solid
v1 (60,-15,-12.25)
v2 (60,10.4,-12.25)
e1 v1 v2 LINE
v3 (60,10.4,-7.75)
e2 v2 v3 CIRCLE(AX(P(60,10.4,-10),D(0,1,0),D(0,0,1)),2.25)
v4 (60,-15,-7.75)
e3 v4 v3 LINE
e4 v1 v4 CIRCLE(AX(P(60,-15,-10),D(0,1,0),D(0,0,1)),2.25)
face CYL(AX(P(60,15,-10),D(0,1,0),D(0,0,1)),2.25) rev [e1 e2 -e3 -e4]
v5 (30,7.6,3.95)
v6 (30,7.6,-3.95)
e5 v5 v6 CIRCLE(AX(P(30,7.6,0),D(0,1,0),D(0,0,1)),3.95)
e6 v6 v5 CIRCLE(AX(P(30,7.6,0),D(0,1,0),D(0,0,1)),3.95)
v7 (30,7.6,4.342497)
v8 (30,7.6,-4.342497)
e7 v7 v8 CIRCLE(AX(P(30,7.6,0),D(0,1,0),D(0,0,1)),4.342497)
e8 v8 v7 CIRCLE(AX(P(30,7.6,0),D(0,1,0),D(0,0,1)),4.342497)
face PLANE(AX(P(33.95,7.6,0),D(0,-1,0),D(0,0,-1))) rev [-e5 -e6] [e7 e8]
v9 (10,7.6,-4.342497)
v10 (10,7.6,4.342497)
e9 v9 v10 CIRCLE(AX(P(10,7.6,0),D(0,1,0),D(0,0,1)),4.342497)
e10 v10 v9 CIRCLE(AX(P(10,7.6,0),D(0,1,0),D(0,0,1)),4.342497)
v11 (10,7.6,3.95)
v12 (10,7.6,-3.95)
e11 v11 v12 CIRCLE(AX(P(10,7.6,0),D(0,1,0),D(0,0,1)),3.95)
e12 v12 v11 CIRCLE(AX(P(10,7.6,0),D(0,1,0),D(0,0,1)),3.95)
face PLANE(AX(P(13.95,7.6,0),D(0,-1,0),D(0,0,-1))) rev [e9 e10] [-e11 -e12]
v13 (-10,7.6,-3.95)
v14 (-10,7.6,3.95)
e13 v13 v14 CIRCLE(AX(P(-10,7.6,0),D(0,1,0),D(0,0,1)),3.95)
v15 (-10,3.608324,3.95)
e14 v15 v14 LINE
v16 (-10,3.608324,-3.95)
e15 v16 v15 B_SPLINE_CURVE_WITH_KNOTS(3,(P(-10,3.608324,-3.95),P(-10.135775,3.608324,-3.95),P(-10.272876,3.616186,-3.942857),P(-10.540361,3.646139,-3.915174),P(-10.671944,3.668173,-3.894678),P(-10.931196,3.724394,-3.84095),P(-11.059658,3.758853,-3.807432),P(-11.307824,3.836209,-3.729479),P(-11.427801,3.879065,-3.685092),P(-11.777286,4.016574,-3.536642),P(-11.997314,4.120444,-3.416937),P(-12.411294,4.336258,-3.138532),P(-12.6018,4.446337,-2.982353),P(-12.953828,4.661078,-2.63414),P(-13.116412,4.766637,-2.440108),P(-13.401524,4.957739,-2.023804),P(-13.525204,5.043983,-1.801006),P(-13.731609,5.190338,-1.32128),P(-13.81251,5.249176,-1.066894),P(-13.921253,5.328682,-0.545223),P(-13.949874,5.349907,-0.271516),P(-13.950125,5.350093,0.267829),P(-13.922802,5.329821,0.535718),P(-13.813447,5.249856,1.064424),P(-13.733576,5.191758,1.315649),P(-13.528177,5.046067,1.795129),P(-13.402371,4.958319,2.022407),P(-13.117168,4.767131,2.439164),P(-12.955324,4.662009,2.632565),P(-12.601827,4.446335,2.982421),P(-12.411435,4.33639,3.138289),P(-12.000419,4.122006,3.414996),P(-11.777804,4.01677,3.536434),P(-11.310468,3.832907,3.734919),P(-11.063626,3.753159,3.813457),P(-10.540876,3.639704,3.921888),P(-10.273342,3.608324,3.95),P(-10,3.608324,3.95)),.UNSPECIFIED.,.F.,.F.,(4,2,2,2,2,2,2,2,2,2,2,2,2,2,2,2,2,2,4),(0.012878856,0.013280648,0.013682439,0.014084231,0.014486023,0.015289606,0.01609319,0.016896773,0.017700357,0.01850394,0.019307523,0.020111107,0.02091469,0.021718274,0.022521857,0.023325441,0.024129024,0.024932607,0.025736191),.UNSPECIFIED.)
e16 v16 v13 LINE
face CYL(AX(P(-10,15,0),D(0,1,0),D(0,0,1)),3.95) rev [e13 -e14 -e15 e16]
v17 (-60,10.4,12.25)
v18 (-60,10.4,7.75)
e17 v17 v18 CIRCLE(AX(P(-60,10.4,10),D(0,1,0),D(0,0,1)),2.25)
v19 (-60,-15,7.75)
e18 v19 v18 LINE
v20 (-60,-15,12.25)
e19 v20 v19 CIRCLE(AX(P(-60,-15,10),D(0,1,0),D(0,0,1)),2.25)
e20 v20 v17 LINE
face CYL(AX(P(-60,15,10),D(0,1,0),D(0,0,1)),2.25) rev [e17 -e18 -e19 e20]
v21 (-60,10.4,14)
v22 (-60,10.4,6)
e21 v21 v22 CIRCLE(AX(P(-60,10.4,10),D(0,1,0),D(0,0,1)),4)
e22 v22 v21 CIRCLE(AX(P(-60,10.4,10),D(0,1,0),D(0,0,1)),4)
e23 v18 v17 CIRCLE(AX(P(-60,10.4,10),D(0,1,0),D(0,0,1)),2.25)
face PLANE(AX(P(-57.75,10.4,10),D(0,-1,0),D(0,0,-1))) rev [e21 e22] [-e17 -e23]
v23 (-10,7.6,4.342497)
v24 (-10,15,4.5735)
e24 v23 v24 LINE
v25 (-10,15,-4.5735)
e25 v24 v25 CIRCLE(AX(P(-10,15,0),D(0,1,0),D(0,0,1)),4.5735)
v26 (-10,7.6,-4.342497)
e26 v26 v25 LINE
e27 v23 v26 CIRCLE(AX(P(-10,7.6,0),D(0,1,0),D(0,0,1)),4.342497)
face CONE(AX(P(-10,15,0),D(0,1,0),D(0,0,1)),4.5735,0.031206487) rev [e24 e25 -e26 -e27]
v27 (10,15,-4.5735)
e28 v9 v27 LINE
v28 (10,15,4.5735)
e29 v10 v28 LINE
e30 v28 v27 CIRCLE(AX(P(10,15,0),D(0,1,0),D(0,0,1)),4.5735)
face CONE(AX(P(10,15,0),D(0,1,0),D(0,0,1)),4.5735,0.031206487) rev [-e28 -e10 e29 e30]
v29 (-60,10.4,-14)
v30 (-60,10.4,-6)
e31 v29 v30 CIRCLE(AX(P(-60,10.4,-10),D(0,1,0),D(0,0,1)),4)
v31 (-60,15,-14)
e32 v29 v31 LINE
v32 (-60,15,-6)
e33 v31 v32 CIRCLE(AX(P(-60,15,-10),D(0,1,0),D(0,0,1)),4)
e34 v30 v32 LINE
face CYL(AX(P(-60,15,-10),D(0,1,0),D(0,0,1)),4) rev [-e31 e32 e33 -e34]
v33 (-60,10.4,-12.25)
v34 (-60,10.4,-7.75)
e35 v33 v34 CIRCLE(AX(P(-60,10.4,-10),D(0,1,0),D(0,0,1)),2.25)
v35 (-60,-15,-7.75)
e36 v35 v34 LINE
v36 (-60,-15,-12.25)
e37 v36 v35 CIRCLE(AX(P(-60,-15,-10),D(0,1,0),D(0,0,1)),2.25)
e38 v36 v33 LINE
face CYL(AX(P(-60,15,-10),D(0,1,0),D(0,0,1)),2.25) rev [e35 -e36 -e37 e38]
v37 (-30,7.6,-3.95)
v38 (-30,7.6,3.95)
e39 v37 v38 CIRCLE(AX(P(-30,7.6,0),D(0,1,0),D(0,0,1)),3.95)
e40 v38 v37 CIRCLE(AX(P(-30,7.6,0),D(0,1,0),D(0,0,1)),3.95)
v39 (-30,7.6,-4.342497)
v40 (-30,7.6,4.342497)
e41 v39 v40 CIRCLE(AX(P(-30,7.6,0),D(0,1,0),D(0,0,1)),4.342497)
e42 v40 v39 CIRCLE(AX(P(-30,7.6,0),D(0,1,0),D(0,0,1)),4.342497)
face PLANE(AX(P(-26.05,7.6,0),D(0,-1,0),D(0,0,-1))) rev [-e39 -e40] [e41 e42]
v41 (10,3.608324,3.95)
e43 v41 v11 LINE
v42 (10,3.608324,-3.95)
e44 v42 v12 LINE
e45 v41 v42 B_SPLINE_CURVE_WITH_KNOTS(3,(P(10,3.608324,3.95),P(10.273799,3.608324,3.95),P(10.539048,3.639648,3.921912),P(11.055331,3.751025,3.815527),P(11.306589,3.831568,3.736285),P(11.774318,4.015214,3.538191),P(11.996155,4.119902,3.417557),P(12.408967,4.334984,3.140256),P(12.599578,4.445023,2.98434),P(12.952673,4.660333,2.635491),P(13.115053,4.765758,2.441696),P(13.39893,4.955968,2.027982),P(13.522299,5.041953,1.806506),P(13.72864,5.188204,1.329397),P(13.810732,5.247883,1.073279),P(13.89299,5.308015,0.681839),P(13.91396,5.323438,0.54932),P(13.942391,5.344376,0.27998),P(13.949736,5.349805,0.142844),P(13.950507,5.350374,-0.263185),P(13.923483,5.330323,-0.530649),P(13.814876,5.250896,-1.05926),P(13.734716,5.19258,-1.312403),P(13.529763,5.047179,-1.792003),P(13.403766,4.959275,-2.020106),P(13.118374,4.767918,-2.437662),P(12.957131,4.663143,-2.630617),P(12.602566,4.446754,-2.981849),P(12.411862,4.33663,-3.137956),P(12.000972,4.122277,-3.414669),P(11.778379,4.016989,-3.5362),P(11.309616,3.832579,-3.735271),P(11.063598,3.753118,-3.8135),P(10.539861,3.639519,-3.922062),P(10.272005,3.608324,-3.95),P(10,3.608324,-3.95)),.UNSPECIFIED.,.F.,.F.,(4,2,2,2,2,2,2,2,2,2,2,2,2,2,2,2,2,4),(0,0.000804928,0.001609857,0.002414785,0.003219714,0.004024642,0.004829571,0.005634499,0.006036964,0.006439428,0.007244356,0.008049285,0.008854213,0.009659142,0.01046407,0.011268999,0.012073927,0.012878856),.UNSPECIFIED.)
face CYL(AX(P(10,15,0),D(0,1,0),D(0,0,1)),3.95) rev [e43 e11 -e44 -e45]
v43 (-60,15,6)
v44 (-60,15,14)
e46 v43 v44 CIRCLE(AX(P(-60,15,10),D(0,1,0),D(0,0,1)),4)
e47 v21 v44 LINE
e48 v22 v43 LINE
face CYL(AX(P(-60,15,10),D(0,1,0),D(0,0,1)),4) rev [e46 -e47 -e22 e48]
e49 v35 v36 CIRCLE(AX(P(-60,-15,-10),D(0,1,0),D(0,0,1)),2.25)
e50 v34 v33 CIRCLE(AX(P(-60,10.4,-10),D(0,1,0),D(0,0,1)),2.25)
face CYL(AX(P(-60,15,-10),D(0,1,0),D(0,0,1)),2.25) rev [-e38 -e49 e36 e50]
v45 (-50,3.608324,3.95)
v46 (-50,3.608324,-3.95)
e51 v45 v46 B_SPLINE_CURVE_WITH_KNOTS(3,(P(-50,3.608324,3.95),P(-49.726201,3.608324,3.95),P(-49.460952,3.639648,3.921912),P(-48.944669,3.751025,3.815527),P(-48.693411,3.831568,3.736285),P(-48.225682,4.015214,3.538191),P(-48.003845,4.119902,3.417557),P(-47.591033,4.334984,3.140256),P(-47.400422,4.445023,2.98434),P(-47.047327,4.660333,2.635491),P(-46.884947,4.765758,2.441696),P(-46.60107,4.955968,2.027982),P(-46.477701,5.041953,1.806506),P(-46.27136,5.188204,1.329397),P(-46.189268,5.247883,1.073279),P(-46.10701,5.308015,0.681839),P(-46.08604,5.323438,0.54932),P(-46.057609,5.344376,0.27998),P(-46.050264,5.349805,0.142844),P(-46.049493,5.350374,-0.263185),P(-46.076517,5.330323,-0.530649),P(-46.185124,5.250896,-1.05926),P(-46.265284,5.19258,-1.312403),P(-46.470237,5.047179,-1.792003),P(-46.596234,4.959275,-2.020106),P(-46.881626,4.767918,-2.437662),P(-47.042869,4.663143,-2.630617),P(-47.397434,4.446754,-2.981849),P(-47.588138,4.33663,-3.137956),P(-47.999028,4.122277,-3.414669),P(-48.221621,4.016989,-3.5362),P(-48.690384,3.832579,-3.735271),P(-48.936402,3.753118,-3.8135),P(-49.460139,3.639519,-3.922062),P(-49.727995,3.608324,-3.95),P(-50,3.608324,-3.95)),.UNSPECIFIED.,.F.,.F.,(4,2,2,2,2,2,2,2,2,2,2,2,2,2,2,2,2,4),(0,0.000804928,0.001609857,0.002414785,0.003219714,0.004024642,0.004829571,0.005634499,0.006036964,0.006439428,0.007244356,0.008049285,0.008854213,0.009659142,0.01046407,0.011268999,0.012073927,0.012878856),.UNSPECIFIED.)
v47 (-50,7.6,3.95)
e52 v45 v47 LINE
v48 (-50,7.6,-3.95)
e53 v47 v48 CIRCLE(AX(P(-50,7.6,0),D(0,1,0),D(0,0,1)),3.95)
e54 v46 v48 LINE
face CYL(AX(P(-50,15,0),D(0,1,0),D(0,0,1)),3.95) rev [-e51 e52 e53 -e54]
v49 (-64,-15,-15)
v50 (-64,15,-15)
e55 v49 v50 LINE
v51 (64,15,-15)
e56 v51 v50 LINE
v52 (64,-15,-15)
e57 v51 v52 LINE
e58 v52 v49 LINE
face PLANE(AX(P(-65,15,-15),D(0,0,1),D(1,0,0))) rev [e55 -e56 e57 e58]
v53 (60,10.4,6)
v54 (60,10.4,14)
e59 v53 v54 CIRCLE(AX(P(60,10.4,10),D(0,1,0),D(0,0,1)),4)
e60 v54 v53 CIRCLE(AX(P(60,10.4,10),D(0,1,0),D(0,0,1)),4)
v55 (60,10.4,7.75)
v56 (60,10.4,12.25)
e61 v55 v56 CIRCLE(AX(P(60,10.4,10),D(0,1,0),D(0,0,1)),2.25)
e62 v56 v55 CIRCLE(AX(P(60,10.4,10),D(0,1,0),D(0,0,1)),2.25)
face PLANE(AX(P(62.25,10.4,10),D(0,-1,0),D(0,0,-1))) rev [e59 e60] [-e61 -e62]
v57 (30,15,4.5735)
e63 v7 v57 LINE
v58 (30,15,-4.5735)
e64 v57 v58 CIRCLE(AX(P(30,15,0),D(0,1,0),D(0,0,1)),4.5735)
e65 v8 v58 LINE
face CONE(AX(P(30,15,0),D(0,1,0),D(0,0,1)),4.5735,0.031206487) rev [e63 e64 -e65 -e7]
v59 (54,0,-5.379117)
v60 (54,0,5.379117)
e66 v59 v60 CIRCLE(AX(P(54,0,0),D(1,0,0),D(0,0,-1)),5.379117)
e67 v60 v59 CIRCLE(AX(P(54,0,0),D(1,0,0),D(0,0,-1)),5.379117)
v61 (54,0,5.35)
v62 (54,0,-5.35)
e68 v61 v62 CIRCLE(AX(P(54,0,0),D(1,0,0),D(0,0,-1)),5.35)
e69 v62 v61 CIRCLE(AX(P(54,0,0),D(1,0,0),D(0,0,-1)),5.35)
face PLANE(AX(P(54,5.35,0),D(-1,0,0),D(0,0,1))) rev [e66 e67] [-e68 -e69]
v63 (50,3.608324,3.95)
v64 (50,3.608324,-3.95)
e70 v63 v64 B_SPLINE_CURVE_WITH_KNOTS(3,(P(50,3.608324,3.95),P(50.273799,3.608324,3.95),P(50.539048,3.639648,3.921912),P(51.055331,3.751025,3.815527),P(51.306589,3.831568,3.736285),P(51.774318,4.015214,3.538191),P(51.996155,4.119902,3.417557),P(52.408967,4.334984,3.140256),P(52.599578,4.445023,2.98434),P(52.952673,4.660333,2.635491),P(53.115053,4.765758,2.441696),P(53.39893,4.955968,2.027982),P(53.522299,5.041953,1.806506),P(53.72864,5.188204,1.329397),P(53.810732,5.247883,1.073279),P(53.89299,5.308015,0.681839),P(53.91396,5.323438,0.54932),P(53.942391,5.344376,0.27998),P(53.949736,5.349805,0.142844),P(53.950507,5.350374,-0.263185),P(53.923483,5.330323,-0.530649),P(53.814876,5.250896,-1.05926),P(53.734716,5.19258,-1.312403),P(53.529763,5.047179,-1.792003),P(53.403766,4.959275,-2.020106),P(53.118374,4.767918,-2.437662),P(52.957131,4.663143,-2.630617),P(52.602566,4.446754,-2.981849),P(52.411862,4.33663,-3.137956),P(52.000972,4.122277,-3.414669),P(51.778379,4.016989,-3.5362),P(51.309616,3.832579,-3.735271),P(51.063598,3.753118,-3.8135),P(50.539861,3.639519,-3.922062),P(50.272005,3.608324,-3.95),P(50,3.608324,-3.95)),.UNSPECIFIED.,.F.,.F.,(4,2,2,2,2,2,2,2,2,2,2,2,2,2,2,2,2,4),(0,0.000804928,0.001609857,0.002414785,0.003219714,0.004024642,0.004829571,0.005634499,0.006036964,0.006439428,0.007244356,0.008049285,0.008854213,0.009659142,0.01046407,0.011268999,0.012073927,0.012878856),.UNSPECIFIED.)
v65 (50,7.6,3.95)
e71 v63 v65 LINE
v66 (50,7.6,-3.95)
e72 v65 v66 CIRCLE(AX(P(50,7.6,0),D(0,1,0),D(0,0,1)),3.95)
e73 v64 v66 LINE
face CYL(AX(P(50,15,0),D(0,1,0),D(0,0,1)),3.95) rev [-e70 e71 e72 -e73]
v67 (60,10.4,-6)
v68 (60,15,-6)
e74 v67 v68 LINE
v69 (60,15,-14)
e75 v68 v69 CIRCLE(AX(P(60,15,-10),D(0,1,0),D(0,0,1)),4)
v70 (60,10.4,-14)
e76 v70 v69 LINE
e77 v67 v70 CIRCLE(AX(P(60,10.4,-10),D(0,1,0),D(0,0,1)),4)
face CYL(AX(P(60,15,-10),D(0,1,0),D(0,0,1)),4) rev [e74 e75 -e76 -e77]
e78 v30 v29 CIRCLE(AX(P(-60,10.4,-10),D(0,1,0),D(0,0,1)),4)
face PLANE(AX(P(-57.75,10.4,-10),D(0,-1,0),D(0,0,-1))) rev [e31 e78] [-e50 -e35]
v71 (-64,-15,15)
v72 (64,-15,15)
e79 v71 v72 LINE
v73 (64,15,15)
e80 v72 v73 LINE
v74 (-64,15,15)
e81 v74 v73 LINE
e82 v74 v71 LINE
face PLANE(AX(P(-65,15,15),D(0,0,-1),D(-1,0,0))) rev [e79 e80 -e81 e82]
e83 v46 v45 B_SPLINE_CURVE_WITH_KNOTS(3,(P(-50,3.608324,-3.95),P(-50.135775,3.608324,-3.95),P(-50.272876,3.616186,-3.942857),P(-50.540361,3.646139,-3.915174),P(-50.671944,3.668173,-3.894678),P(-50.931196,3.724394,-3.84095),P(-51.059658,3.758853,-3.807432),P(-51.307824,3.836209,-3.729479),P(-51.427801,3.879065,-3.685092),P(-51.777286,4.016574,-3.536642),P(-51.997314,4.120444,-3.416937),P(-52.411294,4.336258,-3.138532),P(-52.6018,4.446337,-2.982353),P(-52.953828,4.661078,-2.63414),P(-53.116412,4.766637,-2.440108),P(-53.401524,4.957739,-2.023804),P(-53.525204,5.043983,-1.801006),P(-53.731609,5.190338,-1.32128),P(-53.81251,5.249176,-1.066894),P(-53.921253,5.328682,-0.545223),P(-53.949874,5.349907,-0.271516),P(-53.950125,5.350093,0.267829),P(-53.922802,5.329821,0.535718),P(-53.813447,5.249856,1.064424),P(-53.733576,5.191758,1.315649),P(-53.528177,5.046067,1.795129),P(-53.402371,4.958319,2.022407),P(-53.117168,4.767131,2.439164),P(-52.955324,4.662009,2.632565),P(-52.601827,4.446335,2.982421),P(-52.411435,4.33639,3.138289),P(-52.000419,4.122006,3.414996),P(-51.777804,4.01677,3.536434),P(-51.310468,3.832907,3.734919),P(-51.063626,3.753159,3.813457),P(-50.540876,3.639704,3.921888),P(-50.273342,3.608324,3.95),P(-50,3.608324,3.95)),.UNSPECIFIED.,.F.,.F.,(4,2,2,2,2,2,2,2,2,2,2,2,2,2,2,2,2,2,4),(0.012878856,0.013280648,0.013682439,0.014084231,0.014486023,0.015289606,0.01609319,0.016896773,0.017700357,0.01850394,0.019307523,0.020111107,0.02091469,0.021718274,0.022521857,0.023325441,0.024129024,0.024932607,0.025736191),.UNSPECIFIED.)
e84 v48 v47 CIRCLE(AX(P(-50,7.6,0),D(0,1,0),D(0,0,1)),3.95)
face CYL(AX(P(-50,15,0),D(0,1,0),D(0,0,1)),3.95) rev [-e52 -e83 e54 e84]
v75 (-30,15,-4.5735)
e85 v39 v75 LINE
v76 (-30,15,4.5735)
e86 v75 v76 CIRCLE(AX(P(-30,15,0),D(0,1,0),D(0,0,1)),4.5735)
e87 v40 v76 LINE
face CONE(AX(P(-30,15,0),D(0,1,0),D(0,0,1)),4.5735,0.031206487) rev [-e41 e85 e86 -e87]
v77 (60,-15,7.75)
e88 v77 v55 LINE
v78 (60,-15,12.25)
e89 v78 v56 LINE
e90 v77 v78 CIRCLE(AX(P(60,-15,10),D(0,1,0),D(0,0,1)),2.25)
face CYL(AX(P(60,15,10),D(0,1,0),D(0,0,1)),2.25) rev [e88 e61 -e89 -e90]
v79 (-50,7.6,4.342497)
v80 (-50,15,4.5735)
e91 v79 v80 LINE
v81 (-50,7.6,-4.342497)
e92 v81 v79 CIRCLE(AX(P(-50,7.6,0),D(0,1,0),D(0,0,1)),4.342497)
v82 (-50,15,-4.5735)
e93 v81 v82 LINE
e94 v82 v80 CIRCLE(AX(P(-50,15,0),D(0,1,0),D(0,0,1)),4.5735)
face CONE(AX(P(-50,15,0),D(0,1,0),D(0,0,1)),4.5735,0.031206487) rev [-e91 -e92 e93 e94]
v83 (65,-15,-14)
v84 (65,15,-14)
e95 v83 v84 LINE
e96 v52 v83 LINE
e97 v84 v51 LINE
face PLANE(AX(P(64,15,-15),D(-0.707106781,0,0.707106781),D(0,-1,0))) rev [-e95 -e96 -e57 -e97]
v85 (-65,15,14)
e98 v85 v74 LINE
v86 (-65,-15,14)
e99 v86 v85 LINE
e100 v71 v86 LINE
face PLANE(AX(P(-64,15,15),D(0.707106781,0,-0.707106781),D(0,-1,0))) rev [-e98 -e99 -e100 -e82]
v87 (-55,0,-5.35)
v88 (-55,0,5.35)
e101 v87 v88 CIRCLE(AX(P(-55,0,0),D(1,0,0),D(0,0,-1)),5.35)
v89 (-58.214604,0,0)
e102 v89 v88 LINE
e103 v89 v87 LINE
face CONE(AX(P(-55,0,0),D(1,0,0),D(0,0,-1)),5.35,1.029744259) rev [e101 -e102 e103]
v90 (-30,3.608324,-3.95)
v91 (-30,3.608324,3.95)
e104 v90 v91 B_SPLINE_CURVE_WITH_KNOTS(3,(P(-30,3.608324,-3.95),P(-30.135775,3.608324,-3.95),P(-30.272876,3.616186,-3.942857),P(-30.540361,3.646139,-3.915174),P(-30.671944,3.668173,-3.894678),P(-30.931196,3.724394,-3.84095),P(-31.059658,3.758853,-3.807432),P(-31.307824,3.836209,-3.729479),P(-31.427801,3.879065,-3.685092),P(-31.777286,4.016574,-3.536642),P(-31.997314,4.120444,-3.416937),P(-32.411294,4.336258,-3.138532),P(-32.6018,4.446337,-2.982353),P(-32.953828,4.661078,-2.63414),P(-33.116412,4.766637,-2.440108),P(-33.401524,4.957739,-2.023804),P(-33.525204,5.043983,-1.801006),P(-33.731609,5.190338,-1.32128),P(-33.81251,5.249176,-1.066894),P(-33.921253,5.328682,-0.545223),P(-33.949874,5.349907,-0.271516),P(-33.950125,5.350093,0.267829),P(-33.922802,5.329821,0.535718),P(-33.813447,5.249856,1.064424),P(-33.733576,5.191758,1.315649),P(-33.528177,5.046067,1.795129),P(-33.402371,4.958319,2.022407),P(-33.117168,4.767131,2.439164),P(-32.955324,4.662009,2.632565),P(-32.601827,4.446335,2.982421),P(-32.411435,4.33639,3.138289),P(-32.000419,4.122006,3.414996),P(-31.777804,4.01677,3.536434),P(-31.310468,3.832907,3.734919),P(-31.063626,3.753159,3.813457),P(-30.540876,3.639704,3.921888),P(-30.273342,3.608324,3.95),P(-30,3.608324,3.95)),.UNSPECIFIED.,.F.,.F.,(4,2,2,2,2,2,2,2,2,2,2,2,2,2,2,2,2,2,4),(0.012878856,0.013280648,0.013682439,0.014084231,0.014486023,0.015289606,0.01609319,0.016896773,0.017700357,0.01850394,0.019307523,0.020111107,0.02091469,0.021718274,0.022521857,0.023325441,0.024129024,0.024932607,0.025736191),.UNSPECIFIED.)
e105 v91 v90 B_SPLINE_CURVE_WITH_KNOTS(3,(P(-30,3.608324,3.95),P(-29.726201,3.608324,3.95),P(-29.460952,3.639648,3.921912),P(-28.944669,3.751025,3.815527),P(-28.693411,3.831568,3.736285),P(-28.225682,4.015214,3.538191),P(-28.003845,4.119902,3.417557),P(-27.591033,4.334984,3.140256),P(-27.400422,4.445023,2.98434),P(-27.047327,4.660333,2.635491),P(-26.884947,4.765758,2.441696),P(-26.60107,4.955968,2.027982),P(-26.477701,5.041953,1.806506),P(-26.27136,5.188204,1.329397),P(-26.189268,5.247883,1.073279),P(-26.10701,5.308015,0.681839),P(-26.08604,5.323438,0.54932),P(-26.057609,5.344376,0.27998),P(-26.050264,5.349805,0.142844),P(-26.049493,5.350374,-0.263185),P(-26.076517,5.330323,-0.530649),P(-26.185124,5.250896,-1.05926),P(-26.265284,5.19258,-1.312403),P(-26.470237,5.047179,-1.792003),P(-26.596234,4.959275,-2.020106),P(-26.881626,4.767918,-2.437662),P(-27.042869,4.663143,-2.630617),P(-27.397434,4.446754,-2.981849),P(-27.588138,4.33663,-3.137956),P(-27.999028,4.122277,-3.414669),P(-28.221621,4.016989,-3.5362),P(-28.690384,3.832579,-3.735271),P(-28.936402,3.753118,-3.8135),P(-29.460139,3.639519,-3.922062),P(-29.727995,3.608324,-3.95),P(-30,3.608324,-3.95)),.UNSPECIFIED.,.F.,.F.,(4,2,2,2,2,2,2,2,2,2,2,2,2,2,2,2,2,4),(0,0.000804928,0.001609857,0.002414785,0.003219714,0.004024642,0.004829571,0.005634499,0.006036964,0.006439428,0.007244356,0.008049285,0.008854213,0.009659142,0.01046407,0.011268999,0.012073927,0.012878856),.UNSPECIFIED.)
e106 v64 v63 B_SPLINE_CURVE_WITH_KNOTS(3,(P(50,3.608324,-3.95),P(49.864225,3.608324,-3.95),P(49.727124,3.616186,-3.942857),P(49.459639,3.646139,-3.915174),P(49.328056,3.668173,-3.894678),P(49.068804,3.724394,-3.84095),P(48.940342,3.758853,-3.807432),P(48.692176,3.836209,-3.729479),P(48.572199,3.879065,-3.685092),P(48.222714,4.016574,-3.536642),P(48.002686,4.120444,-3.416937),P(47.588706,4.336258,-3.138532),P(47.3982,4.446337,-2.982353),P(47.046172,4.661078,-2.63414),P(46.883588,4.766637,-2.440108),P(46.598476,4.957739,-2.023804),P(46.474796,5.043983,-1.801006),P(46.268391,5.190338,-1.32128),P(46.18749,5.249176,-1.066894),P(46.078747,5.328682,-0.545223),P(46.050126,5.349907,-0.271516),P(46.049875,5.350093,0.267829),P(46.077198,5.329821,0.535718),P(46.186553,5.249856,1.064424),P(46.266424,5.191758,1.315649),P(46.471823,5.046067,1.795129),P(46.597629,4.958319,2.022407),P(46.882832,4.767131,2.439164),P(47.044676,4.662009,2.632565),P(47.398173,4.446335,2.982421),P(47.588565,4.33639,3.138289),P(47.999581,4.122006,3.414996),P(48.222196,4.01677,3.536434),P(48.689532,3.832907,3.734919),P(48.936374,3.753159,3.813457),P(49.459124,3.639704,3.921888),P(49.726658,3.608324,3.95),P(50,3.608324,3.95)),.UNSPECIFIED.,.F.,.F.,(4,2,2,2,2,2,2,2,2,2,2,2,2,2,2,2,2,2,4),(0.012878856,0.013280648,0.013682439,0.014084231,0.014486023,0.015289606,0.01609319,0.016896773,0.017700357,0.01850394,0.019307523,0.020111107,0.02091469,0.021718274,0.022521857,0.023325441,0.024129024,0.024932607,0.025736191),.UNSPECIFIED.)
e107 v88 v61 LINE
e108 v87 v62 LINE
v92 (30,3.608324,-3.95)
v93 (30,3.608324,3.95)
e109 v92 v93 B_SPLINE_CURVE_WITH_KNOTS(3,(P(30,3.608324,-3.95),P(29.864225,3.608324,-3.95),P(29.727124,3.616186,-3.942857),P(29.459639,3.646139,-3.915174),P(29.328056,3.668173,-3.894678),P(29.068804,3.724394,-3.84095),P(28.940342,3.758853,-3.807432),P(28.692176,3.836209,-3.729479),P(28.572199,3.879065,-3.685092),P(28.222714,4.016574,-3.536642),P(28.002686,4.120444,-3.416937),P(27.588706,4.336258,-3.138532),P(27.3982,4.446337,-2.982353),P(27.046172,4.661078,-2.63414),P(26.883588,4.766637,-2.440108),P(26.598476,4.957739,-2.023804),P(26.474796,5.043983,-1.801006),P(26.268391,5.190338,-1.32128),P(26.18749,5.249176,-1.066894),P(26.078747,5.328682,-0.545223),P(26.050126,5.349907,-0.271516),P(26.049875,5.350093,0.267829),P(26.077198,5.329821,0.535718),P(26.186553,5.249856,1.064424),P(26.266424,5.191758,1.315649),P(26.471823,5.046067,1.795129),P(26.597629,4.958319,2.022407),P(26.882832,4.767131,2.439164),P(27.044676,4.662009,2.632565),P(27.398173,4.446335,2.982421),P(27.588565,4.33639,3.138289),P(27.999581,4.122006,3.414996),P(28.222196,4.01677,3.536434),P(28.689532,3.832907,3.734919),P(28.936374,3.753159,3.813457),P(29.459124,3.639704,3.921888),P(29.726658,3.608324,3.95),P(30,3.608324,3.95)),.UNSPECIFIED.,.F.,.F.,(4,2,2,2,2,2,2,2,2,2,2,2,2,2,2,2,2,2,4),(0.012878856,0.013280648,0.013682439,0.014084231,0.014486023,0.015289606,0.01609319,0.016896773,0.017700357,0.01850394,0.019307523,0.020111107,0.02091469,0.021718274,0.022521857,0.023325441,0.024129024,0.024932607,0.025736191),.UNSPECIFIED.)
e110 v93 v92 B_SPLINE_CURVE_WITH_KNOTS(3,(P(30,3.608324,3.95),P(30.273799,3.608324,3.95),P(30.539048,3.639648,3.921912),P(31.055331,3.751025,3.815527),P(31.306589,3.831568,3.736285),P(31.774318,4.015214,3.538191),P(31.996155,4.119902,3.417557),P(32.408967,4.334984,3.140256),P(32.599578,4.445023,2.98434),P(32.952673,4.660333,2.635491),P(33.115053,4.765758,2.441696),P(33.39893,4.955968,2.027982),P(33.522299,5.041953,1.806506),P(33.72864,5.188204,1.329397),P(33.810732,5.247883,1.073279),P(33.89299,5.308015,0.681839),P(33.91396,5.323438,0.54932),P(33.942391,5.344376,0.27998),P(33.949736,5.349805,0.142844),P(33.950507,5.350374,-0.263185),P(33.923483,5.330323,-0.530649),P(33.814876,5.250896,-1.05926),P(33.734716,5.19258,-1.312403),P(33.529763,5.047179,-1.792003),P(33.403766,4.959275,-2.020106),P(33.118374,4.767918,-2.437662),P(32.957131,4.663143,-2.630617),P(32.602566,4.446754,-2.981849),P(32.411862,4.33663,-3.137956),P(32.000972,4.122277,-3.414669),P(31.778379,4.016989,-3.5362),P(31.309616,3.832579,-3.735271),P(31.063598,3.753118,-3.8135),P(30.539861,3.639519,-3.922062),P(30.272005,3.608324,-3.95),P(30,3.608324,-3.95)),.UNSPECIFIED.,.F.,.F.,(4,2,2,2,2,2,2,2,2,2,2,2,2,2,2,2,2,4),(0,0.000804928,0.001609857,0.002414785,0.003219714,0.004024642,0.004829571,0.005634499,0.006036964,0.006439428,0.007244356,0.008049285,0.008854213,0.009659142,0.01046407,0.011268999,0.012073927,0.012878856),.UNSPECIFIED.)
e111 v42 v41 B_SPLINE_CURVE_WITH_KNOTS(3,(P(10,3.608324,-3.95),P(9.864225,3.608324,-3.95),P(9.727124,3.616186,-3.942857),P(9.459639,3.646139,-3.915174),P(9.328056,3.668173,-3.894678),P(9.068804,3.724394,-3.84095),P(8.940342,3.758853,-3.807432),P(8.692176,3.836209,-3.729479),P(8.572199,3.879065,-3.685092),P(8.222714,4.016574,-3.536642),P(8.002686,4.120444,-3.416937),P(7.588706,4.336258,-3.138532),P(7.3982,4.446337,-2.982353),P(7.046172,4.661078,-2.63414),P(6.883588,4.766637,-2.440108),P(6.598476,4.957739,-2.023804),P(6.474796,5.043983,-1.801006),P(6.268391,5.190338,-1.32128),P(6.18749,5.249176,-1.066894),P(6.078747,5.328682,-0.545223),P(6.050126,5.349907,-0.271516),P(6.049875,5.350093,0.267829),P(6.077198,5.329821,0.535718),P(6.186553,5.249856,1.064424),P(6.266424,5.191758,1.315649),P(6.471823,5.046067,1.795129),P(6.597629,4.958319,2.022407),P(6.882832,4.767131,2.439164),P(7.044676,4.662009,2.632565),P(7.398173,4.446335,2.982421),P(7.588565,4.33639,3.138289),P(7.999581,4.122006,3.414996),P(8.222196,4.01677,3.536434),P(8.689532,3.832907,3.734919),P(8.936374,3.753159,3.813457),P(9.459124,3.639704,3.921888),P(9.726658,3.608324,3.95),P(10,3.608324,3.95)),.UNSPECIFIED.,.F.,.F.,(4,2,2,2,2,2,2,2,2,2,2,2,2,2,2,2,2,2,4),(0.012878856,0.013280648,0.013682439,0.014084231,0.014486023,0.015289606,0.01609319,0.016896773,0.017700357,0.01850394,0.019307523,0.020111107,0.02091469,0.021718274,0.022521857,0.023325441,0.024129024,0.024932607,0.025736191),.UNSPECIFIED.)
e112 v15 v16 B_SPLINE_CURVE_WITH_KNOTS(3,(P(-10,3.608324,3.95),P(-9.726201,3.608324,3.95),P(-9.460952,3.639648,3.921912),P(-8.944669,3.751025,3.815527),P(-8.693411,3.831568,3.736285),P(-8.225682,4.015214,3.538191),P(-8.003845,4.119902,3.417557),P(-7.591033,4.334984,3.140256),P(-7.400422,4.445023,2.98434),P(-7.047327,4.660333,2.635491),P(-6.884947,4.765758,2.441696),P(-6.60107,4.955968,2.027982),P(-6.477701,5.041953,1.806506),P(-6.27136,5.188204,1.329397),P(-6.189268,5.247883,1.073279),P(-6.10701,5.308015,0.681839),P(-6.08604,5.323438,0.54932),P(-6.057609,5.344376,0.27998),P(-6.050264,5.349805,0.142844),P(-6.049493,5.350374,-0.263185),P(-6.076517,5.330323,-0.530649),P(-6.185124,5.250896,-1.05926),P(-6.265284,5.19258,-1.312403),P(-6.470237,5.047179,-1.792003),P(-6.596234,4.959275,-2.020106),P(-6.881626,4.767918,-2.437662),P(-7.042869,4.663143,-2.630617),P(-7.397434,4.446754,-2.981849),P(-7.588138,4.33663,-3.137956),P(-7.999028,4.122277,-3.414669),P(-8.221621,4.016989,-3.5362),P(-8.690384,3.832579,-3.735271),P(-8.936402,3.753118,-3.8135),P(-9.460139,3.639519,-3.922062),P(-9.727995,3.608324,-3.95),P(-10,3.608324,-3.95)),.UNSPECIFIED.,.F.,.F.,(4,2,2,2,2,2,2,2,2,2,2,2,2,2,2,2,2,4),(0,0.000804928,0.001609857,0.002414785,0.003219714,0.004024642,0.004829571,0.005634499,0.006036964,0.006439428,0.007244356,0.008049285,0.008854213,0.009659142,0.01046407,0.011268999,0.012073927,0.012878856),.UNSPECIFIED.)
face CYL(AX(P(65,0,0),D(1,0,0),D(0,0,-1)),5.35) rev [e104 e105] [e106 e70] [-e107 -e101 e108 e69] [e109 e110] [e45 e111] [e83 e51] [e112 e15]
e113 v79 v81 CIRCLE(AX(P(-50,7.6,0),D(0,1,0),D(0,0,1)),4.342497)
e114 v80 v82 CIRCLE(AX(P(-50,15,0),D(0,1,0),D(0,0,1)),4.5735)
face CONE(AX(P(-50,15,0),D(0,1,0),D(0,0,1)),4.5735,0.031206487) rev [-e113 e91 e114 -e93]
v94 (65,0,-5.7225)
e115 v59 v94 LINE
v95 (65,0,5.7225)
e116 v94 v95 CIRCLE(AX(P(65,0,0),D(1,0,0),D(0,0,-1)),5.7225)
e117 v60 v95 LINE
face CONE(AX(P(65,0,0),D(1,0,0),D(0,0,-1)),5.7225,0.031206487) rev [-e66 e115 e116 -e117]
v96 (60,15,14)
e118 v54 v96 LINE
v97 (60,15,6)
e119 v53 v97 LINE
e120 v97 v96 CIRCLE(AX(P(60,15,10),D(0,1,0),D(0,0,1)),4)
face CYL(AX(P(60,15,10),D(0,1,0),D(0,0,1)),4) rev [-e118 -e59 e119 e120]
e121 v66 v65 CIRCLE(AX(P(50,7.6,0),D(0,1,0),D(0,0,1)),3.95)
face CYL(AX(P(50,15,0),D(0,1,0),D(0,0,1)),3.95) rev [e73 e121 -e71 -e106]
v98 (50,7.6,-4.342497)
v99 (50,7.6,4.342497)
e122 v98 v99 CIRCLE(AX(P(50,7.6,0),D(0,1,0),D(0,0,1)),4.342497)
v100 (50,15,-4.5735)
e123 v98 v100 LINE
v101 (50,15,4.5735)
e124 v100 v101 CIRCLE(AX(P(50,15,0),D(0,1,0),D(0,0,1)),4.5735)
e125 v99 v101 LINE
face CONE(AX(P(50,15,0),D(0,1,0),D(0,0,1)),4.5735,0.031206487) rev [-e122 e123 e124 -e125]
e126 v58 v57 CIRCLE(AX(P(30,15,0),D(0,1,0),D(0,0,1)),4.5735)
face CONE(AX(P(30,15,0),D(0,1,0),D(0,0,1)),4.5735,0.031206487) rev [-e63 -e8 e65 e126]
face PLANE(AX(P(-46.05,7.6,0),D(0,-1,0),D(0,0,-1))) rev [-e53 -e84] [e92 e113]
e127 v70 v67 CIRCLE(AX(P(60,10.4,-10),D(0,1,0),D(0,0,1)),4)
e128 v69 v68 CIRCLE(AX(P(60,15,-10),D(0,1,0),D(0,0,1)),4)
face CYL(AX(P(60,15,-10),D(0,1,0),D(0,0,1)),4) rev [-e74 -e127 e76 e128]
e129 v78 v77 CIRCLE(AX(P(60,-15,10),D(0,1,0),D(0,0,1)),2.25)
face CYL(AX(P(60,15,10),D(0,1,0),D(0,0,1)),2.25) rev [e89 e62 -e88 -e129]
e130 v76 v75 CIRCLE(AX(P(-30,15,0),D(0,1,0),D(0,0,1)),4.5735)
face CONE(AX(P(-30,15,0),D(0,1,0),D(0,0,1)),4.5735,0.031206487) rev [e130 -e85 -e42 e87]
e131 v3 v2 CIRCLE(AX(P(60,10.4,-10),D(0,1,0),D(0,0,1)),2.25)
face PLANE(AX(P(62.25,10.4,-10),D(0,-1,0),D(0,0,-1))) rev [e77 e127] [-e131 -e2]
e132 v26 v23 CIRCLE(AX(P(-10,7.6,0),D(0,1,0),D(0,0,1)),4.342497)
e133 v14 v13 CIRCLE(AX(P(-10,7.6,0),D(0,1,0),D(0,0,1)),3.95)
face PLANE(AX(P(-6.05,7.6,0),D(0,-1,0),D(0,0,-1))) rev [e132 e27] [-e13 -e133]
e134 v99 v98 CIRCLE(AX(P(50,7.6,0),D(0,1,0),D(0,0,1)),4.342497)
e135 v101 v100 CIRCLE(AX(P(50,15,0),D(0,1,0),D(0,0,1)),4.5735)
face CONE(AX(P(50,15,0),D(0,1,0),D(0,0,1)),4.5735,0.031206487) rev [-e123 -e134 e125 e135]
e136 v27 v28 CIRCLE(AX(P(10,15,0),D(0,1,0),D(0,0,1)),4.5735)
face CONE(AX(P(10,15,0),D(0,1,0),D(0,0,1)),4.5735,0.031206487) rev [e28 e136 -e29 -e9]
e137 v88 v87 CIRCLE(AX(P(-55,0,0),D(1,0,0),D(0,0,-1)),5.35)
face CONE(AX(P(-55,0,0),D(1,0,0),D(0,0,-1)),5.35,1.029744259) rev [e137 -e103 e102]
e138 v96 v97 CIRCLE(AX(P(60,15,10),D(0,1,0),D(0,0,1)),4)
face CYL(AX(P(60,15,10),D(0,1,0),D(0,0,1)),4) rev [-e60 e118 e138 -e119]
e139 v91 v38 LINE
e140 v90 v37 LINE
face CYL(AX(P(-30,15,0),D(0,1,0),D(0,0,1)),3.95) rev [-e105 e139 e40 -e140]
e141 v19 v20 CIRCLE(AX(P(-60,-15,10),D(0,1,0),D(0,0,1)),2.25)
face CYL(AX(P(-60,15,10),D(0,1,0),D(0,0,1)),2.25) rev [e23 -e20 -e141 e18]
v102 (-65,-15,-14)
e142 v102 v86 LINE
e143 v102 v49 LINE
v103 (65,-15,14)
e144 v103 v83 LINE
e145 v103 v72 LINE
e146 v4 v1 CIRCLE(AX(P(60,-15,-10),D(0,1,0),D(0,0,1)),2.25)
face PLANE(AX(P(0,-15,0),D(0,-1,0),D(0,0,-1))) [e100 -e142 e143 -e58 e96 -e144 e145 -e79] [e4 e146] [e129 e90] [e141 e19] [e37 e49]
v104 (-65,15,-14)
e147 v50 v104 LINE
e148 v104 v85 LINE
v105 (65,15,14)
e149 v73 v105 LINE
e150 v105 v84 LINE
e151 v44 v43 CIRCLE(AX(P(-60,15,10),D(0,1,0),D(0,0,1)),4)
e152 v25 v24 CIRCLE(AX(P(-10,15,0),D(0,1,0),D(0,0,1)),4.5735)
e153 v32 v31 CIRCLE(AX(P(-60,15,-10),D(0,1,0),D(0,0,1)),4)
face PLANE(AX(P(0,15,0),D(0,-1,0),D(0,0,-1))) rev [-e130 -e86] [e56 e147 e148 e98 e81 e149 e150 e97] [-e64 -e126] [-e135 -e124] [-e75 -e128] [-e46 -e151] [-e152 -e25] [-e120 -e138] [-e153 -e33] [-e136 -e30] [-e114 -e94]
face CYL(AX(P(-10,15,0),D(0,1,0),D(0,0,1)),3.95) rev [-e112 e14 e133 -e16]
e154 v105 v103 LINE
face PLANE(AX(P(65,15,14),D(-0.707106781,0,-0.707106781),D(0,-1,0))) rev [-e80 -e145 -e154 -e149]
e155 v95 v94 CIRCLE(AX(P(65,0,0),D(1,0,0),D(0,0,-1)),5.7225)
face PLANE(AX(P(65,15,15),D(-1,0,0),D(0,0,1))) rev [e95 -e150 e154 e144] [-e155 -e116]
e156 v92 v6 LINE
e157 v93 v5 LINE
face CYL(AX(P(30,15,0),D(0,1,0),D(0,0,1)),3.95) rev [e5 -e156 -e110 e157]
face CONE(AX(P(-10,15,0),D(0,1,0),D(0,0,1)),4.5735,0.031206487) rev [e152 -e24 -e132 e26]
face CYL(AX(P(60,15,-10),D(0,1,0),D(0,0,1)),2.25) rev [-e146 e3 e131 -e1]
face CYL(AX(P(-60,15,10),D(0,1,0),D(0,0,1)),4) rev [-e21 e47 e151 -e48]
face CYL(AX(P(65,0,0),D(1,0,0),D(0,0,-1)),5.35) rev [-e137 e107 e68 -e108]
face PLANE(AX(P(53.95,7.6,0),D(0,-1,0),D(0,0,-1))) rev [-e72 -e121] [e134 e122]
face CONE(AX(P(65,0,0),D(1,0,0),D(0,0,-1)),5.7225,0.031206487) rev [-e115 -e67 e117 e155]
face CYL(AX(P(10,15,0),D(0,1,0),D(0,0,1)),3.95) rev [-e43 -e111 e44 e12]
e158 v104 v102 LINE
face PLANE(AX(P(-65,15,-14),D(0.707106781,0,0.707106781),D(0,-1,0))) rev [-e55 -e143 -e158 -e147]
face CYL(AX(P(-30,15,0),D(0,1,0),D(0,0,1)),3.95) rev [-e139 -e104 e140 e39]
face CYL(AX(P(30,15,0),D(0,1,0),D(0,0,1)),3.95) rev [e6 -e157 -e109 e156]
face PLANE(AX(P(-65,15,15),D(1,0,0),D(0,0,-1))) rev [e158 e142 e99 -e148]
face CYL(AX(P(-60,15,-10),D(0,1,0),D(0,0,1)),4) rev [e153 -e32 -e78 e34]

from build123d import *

# Parameters (mm, degrees)
SKETCH_1_W                = 130
SKETCH_1_H                = 30
EXTRUDE_1_DEPTH           = 15
F_1_8_RC_1_AT_2_COUNT     = 2
F_1_8_RC_1_AT_2_PITCH     = 20
F_1_8_RC_1_AT_3_COUNT     = 2
F_1_8_RC_1_AT_3_PITCH     = 40
F_1_8_RC_1_AT_4_COUNT     = 2
F_1_8_RC_1_AT_4_PITCH     = 60
F_1_8_RC_1_AT_5_COUNT     = 2
F_1_8_RC_1_AT_5_PITCH     = 80
F_1_8_RC_1_AT_6_COUNT     = 2
F_1_8_RC_1_AT_6_PITCH     = 100
CHAMFER_1_SIZE            = 1
HOLE_WIZARD_1_D           = 4.5
HOLE_WIZARD_1_CBORE_D     = 8
HOLE_WIZARD_1_CBORE_DEPTH = 4.6


with BuildPart() as part:
    # 草图1 → 凸台-拉伸1 (new, symmetric)
    with BuildSketch(Plane(origin=(0, 0, 0), x_dir=(1, 0, 0), z_dir=(0, 1, 0))):
        Rectangle(SKETCH_1_W, SKETCH_1_H)
    extrude(amount=EXTRUDE_1_DEPTH, both=True)

    # 草图4 → 1/4 Rc 螺纹孔1 (revolve, cut)
    with BuildSketch(Plane(origin=(65, 0, 0), x_dir=(0, 0, -1), z_dir=(0, 1, 0))):
        Polygon((0, 0), (0, 123.214604312), (5.35, 120), (5.35, 11), (5.379117168, 11), (5.7225, 0), align=None)
    revolve(axis=Axis((71.35, 0, 0), (-1, 0, 0)), mode=Mode.SUBTRACT)

    # 草图8 → 1/8 Rc 螺纹孔1 (revolve, cut)
    with BuildSketch(Plane(origin=(50, 15, 0), x_dir=(0, 0, 1), z_dir=(1, 0, 0))):
        Polygon((0, 0), (0, 14.313399445), (3.95, 11.94), (3.95, 7.4), (4.342497004, 7.4), (4.5735, 0), align=None)
    f_1_8_rc_1 = revolve(axis=Axis((50, 21.35, 0), (0, -1, 0)), mode=Mode.SUBTRACT)

    # 1/8 Rc 螺纹孔1 at 2: 1/8 Rc 螺纹孔1 ×2
    with Locations(*[(-i * F_1_8_RC_1_AT_2_PITCH, 0, 0) for i in range(1, F_1_8_RC_1_AT_2_COUNT)]):
        add(f_1_8_rc_1, mode=Mode.SUBTRACT)

    # 1/8 Rc 螺纹孔1 at 3: 1/8 Rc 螺纹孔1 ×2
    with Locations(*[(-i * F_1_8_RC_1_AT_3_PITCH, 0, 0) for i in range(1, F_1_8_RC_1_AT_3_COUNT)]):
        add(f_1_8_rc_1, mode=Mode.SUBTRACT)

    # 1/8 Rc 螺纹孔1 at 4: 1/8 Rc 螺纹孔1 ×2
    with Locations(*[(-i * F_1_8_RC_1_AT_4_PITCH, 0, 0) for i in range(1, F_1_8_RC_1_AT_4_COUNT)]):
        add(f_1_8_rc_1, mode=Mode.SUBTRACT)

    # 1/8 Rc 螺纹孔1 at 5: 1/8 Rc 螺纹孔1 ×2
    with Locations(*[(-i * F_1_8_RC_1_AT_5_PITCH, 0, 0) for i in range(1, F_1_8_RC_1_AT_5_COUNT)]):
        add(f_1_8_rc_1, mode=Mode.SUBTRACT)

    # 1/8 Rc 螺纹孔1 at 6: 1/8 Rc 螺纹孔1 ×2
    with Locations(*[(-i * F_1_8_RC_1_AT_6_PITCH, 0, 0) for i in range(1, F_1_8_RC_1_AT_6_COUNT)]):
        add(f_1_8_rc_1, mode=Mode.SUBTRACT)

    # 倒角1
    chamfer_1_edges = [part.edges().sort_by_distance(p)[0] for p in [
        (65, 0, 15),
        (-65, 0, 15),
        (-65, 0, -15),
        (65, 0, -15),
    ]]
    chamfer(chamfer_1_edges, length=CHAMFER_1_SIZE)

    # 打孔尺寸(%根据)内六角圆柱头螺钉的类型1 (through all)
    with Locations(Plane(origin=(0, 15, 0), x_dir=(1, 0, 0), z_dir=(0, 1, 0))):
        with Locations((-60, 10), (-60, -10), (60, -10), (60, 10)):
            CounterBoreHole(HOLE_WIZARD_1_D / 2, HOLE_WIZARD_1_CBORE_D / 2, HOLE_WIZARD_1_CBORE_DEPTH)


solid = part.part
